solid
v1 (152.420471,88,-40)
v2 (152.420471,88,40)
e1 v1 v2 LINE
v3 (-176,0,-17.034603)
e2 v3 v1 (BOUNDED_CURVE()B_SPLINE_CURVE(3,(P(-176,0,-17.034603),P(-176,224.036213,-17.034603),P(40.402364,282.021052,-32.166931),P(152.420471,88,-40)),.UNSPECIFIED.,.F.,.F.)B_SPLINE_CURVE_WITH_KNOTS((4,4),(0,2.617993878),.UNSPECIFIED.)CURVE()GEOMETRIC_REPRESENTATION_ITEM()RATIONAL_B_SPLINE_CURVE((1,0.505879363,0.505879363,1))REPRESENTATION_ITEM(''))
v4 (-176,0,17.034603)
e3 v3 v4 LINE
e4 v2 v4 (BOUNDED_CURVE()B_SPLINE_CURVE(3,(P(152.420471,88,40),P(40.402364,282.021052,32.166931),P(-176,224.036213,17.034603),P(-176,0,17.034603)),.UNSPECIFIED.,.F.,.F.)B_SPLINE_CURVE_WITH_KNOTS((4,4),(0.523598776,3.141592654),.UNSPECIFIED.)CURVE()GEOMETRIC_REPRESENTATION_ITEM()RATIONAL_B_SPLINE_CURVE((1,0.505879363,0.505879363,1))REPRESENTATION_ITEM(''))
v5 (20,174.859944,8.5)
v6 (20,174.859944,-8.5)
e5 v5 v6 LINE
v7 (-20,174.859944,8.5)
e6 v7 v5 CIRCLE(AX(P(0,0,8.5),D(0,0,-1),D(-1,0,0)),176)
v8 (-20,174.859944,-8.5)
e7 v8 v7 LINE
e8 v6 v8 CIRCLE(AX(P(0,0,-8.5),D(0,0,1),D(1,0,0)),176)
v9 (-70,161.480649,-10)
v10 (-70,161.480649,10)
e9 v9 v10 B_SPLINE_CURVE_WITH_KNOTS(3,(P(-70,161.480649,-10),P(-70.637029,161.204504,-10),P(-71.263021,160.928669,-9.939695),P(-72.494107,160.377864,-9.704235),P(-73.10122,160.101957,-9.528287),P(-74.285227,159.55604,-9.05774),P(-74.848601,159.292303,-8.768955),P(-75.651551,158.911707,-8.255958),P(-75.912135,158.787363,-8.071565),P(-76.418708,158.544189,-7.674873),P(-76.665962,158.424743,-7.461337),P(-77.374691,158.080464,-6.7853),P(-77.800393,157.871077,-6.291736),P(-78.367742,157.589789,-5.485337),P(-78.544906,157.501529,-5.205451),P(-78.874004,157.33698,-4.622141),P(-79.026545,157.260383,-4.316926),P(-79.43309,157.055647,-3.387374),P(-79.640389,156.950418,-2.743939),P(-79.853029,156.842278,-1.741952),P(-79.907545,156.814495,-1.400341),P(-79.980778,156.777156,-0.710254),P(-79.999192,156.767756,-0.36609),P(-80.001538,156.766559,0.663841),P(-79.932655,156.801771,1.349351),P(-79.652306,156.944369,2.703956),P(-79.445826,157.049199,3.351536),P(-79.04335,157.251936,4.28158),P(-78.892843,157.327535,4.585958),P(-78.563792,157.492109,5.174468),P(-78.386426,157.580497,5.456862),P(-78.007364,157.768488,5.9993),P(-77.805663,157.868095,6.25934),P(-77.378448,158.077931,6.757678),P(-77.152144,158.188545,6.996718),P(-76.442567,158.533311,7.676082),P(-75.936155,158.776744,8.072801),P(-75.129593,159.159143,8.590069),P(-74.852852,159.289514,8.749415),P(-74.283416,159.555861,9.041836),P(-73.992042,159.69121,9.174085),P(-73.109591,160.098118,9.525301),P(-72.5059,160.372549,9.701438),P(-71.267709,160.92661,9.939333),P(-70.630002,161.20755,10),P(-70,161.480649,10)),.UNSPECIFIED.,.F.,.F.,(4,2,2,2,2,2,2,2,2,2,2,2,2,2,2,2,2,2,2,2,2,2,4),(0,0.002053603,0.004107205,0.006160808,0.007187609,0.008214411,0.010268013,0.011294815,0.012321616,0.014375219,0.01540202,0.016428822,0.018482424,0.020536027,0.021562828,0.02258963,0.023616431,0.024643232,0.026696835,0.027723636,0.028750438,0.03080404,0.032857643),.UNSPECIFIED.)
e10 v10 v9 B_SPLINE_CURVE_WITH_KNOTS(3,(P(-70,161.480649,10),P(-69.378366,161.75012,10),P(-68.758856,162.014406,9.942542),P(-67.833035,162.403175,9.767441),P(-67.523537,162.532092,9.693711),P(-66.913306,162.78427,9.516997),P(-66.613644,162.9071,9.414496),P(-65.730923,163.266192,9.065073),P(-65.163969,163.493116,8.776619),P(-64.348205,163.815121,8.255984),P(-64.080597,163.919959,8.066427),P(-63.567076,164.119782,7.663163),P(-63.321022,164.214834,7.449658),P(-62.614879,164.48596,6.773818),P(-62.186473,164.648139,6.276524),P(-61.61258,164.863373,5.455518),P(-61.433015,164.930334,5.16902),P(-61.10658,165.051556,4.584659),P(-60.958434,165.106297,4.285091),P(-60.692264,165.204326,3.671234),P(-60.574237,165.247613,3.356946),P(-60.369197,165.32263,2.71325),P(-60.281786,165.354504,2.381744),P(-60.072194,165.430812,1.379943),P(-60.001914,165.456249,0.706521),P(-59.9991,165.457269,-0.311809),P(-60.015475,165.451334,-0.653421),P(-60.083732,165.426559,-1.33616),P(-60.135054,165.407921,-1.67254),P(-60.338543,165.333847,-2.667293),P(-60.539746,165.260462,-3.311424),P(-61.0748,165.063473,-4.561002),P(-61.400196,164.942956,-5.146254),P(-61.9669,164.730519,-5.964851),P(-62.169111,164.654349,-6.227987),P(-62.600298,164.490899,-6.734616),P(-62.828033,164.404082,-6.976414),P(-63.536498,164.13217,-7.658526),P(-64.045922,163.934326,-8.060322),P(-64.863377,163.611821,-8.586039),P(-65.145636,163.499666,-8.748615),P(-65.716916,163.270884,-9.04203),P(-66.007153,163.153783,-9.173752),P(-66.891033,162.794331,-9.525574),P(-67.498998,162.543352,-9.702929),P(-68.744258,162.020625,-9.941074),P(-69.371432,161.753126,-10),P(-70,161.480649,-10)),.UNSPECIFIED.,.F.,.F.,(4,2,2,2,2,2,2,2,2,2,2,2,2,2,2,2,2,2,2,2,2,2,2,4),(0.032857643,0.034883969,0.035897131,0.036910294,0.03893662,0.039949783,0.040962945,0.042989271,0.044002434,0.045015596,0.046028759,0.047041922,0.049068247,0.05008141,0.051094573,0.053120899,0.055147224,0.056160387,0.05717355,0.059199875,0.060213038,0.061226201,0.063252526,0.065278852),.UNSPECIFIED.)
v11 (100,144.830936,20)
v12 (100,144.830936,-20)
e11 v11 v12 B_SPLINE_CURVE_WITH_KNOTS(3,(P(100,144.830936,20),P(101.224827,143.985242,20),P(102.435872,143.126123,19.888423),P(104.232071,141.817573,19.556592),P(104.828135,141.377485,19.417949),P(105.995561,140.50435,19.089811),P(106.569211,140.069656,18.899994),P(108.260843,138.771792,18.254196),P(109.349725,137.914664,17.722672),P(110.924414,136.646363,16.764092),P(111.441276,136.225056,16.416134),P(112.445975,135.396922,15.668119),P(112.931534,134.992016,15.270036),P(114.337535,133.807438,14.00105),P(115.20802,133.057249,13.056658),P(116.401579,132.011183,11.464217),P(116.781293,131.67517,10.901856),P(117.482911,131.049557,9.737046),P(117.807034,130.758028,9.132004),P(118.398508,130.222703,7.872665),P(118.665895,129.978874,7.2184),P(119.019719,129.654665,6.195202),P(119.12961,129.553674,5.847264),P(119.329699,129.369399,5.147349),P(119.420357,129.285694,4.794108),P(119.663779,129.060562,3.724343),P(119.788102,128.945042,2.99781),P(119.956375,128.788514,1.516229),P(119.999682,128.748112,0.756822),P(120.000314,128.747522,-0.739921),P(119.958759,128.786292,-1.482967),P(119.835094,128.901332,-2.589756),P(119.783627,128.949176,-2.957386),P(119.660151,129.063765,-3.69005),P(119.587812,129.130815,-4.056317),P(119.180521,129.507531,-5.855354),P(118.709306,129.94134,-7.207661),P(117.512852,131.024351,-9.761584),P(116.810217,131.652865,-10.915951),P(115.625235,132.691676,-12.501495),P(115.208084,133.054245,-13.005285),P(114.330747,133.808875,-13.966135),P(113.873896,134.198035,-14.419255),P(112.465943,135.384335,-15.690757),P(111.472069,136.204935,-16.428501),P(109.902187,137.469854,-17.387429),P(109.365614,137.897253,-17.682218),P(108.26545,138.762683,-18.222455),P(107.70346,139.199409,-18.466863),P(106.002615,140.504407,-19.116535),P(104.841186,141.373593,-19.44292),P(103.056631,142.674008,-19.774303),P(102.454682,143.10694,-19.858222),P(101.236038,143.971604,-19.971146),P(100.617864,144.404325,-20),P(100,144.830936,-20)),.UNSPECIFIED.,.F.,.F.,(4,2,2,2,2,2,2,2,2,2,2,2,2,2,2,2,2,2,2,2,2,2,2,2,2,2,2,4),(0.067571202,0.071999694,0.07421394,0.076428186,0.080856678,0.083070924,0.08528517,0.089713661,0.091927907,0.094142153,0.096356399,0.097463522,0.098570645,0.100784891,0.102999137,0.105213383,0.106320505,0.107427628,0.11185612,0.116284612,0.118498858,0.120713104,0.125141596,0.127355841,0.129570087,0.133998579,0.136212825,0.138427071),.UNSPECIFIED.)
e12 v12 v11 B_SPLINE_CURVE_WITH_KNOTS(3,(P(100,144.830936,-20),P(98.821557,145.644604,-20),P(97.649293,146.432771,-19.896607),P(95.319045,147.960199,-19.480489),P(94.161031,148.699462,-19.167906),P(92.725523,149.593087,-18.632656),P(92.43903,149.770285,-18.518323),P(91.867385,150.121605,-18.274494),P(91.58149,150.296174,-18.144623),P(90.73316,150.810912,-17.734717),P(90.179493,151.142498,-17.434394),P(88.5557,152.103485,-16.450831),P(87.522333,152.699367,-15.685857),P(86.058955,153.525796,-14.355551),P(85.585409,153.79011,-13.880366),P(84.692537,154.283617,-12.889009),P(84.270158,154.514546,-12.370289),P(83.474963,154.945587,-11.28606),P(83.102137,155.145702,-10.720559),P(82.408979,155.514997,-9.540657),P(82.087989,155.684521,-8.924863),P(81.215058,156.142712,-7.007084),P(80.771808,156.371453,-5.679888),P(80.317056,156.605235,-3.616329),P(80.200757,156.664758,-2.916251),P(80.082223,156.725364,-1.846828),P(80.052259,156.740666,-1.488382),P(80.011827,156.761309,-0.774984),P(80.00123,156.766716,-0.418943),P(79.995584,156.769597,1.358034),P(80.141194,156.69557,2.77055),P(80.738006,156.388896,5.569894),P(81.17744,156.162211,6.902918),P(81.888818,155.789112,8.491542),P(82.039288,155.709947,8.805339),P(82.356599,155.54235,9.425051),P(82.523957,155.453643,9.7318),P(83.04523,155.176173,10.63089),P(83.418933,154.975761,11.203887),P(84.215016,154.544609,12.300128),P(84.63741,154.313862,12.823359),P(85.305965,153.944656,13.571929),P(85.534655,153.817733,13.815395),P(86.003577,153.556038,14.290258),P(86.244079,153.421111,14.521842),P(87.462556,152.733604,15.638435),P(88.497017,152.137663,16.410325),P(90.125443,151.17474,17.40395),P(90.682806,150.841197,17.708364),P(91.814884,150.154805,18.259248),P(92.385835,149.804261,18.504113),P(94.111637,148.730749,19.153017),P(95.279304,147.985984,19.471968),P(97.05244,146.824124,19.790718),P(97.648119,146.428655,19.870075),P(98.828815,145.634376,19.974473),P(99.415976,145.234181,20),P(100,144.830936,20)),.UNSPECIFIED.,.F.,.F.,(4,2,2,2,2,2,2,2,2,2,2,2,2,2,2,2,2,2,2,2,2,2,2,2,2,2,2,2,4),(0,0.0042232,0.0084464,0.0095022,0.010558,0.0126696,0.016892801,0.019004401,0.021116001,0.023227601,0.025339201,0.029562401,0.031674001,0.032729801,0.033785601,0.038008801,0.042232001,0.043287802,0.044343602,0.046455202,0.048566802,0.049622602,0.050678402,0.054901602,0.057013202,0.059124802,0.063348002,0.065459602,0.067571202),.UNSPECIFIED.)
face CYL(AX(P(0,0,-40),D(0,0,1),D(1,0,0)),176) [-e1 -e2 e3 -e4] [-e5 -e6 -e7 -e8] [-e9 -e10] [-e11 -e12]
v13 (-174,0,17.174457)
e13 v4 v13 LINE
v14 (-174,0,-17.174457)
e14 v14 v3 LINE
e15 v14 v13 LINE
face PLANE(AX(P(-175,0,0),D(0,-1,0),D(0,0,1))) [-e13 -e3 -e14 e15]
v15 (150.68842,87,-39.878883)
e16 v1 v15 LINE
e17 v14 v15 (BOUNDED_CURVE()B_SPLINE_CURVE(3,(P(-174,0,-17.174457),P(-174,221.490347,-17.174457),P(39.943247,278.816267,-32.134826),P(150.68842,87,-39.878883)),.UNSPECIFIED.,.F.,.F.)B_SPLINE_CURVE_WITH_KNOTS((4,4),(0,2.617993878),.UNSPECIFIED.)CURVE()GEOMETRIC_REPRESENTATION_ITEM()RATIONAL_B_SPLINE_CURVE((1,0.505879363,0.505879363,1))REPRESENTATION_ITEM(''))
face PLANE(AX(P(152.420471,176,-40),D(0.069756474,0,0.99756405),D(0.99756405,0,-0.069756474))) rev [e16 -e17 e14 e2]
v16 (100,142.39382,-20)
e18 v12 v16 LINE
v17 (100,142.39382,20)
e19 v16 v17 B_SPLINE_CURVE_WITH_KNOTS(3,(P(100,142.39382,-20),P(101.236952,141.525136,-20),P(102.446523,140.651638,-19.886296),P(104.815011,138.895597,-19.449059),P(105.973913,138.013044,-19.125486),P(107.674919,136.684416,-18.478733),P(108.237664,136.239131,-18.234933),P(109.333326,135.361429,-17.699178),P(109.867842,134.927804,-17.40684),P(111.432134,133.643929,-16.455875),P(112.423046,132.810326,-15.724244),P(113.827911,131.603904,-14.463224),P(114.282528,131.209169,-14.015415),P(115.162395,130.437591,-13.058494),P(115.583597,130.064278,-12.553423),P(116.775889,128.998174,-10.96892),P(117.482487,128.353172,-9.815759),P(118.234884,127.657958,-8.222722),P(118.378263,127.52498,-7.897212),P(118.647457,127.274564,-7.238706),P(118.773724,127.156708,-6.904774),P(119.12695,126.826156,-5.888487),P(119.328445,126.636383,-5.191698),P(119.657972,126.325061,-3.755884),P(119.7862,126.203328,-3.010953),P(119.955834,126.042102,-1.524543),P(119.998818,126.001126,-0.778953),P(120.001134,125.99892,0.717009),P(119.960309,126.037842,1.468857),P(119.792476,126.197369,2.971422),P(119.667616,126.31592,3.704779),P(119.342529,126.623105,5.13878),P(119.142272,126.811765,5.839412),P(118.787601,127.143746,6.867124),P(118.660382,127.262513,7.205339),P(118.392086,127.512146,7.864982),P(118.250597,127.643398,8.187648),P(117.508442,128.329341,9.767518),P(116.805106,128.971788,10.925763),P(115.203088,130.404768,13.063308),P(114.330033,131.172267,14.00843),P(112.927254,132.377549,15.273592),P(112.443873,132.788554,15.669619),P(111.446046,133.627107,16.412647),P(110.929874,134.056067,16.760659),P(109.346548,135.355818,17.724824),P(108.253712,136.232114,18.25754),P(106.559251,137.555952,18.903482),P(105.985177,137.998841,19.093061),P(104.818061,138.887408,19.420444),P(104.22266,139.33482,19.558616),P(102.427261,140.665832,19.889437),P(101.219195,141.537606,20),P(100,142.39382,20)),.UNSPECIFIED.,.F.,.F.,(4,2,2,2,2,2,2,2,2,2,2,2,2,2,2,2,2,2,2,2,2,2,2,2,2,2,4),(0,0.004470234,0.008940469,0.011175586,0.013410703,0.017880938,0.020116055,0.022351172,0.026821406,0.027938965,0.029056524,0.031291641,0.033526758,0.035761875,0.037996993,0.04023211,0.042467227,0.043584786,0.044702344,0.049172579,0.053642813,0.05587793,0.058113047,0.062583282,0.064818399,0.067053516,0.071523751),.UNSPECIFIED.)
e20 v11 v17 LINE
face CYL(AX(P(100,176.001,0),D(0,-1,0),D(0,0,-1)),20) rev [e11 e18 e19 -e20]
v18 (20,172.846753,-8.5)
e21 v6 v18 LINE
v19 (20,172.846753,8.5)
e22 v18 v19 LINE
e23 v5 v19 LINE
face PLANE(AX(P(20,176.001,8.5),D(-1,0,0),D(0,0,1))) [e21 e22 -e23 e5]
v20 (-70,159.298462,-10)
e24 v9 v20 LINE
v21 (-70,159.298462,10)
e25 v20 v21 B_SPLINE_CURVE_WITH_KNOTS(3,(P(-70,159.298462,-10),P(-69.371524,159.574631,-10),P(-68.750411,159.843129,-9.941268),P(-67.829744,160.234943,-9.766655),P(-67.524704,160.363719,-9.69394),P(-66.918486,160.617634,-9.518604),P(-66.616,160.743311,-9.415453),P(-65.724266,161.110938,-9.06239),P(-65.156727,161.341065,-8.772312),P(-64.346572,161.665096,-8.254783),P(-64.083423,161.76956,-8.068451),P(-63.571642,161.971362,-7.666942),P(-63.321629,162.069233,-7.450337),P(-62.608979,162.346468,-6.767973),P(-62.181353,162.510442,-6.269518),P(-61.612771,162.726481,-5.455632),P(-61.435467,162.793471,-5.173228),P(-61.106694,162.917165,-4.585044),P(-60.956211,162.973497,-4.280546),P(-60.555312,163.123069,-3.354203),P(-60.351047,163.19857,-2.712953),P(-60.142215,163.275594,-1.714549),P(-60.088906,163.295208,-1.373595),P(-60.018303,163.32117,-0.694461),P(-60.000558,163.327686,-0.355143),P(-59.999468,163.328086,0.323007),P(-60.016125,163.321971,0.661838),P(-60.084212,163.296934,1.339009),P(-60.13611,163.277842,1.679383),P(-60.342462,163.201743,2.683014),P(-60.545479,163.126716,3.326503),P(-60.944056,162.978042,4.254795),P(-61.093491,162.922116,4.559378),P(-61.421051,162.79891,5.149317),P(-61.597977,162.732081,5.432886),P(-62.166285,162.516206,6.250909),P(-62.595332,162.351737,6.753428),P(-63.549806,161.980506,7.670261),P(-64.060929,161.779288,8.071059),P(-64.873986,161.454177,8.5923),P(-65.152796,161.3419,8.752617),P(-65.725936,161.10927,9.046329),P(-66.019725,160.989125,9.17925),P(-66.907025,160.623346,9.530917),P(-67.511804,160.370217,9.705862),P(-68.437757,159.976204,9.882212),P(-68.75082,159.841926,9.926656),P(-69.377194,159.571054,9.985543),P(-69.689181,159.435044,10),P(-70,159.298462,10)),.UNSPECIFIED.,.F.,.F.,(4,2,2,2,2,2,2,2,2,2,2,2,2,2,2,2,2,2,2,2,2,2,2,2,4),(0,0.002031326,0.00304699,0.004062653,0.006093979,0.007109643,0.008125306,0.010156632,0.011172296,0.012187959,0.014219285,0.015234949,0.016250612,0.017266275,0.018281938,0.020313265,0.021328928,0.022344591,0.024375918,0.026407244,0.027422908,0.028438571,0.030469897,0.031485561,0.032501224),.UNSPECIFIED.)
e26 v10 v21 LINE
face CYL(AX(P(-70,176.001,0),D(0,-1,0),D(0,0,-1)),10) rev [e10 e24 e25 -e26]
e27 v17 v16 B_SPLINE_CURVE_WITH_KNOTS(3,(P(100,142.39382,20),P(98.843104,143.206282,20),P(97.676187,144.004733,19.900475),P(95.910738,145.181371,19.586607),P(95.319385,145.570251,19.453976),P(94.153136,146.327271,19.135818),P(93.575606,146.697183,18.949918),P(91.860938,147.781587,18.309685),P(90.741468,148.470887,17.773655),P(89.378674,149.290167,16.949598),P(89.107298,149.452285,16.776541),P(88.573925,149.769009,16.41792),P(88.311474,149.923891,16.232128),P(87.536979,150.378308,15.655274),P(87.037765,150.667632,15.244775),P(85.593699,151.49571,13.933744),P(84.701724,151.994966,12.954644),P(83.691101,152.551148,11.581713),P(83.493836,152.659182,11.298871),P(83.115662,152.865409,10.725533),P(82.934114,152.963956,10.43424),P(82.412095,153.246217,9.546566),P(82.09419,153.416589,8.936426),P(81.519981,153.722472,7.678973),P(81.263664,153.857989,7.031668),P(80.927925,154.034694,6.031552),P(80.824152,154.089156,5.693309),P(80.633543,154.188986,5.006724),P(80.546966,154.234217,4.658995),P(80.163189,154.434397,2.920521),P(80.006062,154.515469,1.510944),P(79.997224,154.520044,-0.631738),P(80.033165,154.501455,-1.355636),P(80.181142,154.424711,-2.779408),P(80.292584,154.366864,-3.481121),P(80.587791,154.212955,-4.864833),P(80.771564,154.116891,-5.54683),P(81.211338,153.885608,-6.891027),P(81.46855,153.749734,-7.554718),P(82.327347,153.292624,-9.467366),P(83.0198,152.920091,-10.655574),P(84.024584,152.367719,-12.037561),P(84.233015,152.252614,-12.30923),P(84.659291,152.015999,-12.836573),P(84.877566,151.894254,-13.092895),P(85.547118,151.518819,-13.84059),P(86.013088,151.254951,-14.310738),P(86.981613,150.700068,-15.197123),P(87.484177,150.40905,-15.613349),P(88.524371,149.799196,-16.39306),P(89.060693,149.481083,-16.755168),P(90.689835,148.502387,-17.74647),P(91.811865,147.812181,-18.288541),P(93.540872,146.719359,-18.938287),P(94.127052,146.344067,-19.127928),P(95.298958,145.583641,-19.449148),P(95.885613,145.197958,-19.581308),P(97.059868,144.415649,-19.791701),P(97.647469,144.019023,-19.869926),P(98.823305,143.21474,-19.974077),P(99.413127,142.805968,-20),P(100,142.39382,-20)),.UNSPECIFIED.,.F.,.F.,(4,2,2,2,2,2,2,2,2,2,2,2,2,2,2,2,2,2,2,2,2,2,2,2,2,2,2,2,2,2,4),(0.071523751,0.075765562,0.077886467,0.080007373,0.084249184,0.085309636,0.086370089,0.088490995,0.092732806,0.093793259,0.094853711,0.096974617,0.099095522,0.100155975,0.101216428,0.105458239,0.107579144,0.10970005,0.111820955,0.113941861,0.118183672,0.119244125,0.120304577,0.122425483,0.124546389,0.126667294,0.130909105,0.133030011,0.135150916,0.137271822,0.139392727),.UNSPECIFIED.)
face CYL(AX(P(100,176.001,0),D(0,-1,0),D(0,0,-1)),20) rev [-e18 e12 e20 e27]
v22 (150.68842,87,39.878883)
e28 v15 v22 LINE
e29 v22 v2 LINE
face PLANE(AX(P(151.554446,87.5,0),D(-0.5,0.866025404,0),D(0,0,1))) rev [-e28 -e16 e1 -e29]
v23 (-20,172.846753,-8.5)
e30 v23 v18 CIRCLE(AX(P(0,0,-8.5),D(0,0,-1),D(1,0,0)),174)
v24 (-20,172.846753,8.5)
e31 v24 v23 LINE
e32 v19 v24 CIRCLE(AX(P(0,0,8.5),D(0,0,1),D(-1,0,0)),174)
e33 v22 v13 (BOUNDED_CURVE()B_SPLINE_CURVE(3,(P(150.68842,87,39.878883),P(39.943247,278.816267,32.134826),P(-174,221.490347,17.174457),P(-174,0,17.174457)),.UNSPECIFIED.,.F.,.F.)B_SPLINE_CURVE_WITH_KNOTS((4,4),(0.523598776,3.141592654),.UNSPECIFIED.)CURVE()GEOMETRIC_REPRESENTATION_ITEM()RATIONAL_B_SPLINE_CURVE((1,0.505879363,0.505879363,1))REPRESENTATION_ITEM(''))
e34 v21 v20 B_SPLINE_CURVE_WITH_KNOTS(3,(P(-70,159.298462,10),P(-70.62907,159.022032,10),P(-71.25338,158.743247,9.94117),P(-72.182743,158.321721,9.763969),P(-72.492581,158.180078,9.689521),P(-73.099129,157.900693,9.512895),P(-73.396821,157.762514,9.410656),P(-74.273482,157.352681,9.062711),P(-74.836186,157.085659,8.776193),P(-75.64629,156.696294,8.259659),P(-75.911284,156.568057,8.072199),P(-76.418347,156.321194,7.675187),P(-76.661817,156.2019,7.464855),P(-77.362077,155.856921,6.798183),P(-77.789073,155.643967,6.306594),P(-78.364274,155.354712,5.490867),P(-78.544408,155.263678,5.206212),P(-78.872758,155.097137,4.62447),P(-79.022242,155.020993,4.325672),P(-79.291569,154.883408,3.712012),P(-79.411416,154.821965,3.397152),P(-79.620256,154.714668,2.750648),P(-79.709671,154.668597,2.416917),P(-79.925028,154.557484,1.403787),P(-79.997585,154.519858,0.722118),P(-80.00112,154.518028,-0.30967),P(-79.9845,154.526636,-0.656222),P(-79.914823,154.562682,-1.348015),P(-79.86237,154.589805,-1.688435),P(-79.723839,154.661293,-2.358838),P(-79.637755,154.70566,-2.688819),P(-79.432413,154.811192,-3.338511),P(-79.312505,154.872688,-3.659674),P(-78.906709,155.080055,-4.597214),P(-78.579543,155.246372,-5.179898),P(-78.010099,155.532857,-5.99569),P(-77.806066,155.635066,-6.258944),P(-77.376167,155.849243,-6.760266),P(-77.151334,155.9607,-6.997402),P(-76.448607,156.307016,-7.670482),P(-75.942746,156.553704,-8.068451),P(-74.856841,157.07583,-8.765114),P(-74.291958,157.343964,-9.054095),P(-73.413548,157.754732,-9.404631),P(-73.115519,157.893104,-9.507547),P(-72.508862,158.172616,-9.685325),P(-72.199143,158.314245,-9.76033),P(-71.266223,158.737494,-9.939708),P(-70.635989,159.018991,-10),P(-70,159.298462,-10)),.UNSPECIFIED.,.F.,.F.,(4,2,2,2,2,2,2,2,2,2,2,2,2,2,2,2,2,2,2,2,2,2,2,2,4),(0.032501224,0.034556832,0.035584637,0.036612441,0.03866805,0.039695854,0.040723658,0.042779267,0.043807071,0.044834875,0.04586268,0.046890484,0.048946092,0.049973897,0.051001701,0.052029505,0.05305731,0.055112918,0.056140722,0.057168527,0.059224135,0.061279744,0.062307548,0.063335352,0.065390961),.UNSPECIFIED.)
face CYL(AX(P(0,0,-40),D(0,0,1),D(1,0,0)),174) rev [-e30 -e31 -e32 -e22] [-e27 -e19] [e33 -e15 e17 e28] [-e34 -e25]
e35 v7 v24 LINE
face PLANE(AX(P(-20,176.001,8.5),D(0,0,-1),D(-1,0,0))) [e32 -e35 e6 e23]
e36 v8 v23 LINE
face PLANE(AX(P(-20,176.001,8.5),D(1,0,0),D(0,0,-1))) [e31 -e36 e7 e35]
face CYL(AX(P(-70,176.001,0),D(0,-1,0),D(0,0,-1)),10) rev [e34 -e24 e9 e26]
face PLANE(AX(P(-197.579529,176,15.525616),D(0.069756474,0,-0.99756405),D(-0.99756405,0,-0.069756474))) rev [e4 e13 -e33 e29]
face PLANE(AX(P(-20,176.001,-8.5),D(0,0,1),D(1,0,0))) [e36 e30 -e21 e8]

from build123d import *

# Parameters (mm, degrees)
SHEET_EXTRUDE_1_1_BACK   = 40
SHEET_EXTRUDE_1_1_DEPTH  = 80
THICKEN_1_T1             = 1
THICKEN_1_T2             = 1
SKETCH_2_OUTSIDE_W       = 406.64
SKETCH_2_OUTSIDE_H       = 158.22
CUT_EXTRUDE_1_DEPTH      = 253.095220105
CUT_EXTRUDE_2_REACH      = 254.095
CUT_EXTRUDE_2_END_RADIUS = 176
SKETCH_3_W               = 40
SKETCH_3_H               = 17
CUT_EXTRUDE_3_REACH      = 254.095
CUT_EXTRUDE_3_END_RADIUS = 176
SKETCH_4_R               = 20
CUT_EXTRUDE_4_REACH      = 254.095
SKETCH_5_R               = 10


with BuildPart() as body_1:
    # Sheet Extrude 1: a surface, the sketch's curves swept straight by 80 mm
    with BuildLine(Plane.XY.offset(-SHEET_EXTRUDE_1_1_BACK), mode=Mode.PRIVATE) as sheet_extrude_1_1_path:
        ThreePointArc((151.554445662, 87.5), (-45.293332893, 169.037019601), (-175, 0))
    sheet_extrude_1_1 = Shell.extrude(sheet_extrude_1_1_path.wire(), (0 * SHEET_EXTRUDE_1_1_DEPTH, 0 * SHEET_EXTRUDE_1_1_DEPTH, 1 * SHEET_EXTRUDE_1_1_DEPTH))
    add(Solid.thicken(sheet_extrude_1_1, THICKEN_1_T1))
    add(Solid.thicken(sheet_extrude_1_1, -THICKEN_1_T2))

    # 草图2 outside → 切除-拉伸1 (cut, through all)
    with BuildSketch(Plane(origin=(0, 0, 0), x_dir=(1, 0, 0), z_dir=(0, 1, 0))):
        with Locations((-11.79, 0)):
            Rectangle(SKETCH_2_OUTSIDE_W, SKETCH_2_OUTSIDE_H)
        Polygon((152.420471066, 40), (-197.579528934, 15.52561582), (-197.579528934, -15.52561582), (152.420471066, -40), align=None, mode=Mode.SUBTRACT)
    extrude(amount=CUT_EXTRUDE_1_DEPTH, mode=Mode.SUBTRACT)

    # 切除-拉伸2: up to this cylinder (the profile starts inside it)
    cut_extrude_2_end = Plane(origin=(0, 0, 0), z_dir=(0, 0, 1)) * Cylinder(CUT_EXTRUDE_2_END_RADIUS, 861.19, mode=Mode.PRIVATE)
    # 草图3 → 切除-拉伸2 (cut, up to the surface)
    with BuildSketch(Plane(origin=(0, 0, 0), x_dir=(1, 0, 0), z_dir=(0, 1, 0)), mode=Mode.PRIVATE) as cut_extrude_2_sk1:
        Rectangle(SKETCH_3_W, SKETCH_3_H)
    cut_extrude_2_tool1 = extrude(cut_extrude_2_sk1.sketch, amount=CUT_EXTRUDE_2_REACH, mode=Mode.PRIVATE) & cut_extrude_2_end
    add(cut_extrude_2_tool1.solids().sort_by_distance((0, 0, 0))[0], mode=Mode.SUBTRACT)

    # 切除-拉伸3: up to this cylinder (the profile starts inside it)
    cut_extrude_3_end = Plane(origin=(0, 0, 0), z_dir=(0, 0, 1)) * Cylinder(CUT_EXTRUDE_3_END_RADIUS, 861.19, mode=Mode.PRIVATE)
    # 草图4 → 切除-拉伸3 (cut, up to the surface)
    with BuildSketch(Plane(origin=(0, 0, 0), x_dir=(1, 0, 0), z_dir=(0, 1, 0)), mode=Mode.PRIVATE) as cut_extrude_3_sk1:
        with Locations(Location((100, 0, 0), (0, 0, 90))):
            Circle(SKETCH_4_R)
    cut_extrude_3_tool1 = extrude(cut_extrude_3_sk1.sketch, amount=CUT_EXTRUDE_3_REACH, mode=Mode.PRIVATE) & cut_extrude_3_end
    add(cut_extrude_3_tool1.solids().sort_by_distance((100, 0, 0))[0], mode=Mode.SUBTRACT)

    # 草图5 → 切除-拉伸4 (cut, up to next)
    with BuildSketch(Plane(origin=(0, 0, 0), x_dir=(1, 0, 0), z_dir=(0, 1, 0)), mode=Mode.PRIVATE) as cut_extrude_4_sk1:
        with Locations(Location((-70, 0, 0), (0, 0, 90))):
            Circle(SKETCH_5_R)
    cut_extrude_4_tool1 = extrude(cut_extrude_4_sk1.sketch, amount=CUT_EXTRUDE_4_REACH, mode=Mode.PRIVATE) & body_1.part
    add(cut_extrude_4_tool1.solids().sort_by_distance((-70, 0, 0))[0], mode=Mode.SUBTRACT)


solid = body_1.part
